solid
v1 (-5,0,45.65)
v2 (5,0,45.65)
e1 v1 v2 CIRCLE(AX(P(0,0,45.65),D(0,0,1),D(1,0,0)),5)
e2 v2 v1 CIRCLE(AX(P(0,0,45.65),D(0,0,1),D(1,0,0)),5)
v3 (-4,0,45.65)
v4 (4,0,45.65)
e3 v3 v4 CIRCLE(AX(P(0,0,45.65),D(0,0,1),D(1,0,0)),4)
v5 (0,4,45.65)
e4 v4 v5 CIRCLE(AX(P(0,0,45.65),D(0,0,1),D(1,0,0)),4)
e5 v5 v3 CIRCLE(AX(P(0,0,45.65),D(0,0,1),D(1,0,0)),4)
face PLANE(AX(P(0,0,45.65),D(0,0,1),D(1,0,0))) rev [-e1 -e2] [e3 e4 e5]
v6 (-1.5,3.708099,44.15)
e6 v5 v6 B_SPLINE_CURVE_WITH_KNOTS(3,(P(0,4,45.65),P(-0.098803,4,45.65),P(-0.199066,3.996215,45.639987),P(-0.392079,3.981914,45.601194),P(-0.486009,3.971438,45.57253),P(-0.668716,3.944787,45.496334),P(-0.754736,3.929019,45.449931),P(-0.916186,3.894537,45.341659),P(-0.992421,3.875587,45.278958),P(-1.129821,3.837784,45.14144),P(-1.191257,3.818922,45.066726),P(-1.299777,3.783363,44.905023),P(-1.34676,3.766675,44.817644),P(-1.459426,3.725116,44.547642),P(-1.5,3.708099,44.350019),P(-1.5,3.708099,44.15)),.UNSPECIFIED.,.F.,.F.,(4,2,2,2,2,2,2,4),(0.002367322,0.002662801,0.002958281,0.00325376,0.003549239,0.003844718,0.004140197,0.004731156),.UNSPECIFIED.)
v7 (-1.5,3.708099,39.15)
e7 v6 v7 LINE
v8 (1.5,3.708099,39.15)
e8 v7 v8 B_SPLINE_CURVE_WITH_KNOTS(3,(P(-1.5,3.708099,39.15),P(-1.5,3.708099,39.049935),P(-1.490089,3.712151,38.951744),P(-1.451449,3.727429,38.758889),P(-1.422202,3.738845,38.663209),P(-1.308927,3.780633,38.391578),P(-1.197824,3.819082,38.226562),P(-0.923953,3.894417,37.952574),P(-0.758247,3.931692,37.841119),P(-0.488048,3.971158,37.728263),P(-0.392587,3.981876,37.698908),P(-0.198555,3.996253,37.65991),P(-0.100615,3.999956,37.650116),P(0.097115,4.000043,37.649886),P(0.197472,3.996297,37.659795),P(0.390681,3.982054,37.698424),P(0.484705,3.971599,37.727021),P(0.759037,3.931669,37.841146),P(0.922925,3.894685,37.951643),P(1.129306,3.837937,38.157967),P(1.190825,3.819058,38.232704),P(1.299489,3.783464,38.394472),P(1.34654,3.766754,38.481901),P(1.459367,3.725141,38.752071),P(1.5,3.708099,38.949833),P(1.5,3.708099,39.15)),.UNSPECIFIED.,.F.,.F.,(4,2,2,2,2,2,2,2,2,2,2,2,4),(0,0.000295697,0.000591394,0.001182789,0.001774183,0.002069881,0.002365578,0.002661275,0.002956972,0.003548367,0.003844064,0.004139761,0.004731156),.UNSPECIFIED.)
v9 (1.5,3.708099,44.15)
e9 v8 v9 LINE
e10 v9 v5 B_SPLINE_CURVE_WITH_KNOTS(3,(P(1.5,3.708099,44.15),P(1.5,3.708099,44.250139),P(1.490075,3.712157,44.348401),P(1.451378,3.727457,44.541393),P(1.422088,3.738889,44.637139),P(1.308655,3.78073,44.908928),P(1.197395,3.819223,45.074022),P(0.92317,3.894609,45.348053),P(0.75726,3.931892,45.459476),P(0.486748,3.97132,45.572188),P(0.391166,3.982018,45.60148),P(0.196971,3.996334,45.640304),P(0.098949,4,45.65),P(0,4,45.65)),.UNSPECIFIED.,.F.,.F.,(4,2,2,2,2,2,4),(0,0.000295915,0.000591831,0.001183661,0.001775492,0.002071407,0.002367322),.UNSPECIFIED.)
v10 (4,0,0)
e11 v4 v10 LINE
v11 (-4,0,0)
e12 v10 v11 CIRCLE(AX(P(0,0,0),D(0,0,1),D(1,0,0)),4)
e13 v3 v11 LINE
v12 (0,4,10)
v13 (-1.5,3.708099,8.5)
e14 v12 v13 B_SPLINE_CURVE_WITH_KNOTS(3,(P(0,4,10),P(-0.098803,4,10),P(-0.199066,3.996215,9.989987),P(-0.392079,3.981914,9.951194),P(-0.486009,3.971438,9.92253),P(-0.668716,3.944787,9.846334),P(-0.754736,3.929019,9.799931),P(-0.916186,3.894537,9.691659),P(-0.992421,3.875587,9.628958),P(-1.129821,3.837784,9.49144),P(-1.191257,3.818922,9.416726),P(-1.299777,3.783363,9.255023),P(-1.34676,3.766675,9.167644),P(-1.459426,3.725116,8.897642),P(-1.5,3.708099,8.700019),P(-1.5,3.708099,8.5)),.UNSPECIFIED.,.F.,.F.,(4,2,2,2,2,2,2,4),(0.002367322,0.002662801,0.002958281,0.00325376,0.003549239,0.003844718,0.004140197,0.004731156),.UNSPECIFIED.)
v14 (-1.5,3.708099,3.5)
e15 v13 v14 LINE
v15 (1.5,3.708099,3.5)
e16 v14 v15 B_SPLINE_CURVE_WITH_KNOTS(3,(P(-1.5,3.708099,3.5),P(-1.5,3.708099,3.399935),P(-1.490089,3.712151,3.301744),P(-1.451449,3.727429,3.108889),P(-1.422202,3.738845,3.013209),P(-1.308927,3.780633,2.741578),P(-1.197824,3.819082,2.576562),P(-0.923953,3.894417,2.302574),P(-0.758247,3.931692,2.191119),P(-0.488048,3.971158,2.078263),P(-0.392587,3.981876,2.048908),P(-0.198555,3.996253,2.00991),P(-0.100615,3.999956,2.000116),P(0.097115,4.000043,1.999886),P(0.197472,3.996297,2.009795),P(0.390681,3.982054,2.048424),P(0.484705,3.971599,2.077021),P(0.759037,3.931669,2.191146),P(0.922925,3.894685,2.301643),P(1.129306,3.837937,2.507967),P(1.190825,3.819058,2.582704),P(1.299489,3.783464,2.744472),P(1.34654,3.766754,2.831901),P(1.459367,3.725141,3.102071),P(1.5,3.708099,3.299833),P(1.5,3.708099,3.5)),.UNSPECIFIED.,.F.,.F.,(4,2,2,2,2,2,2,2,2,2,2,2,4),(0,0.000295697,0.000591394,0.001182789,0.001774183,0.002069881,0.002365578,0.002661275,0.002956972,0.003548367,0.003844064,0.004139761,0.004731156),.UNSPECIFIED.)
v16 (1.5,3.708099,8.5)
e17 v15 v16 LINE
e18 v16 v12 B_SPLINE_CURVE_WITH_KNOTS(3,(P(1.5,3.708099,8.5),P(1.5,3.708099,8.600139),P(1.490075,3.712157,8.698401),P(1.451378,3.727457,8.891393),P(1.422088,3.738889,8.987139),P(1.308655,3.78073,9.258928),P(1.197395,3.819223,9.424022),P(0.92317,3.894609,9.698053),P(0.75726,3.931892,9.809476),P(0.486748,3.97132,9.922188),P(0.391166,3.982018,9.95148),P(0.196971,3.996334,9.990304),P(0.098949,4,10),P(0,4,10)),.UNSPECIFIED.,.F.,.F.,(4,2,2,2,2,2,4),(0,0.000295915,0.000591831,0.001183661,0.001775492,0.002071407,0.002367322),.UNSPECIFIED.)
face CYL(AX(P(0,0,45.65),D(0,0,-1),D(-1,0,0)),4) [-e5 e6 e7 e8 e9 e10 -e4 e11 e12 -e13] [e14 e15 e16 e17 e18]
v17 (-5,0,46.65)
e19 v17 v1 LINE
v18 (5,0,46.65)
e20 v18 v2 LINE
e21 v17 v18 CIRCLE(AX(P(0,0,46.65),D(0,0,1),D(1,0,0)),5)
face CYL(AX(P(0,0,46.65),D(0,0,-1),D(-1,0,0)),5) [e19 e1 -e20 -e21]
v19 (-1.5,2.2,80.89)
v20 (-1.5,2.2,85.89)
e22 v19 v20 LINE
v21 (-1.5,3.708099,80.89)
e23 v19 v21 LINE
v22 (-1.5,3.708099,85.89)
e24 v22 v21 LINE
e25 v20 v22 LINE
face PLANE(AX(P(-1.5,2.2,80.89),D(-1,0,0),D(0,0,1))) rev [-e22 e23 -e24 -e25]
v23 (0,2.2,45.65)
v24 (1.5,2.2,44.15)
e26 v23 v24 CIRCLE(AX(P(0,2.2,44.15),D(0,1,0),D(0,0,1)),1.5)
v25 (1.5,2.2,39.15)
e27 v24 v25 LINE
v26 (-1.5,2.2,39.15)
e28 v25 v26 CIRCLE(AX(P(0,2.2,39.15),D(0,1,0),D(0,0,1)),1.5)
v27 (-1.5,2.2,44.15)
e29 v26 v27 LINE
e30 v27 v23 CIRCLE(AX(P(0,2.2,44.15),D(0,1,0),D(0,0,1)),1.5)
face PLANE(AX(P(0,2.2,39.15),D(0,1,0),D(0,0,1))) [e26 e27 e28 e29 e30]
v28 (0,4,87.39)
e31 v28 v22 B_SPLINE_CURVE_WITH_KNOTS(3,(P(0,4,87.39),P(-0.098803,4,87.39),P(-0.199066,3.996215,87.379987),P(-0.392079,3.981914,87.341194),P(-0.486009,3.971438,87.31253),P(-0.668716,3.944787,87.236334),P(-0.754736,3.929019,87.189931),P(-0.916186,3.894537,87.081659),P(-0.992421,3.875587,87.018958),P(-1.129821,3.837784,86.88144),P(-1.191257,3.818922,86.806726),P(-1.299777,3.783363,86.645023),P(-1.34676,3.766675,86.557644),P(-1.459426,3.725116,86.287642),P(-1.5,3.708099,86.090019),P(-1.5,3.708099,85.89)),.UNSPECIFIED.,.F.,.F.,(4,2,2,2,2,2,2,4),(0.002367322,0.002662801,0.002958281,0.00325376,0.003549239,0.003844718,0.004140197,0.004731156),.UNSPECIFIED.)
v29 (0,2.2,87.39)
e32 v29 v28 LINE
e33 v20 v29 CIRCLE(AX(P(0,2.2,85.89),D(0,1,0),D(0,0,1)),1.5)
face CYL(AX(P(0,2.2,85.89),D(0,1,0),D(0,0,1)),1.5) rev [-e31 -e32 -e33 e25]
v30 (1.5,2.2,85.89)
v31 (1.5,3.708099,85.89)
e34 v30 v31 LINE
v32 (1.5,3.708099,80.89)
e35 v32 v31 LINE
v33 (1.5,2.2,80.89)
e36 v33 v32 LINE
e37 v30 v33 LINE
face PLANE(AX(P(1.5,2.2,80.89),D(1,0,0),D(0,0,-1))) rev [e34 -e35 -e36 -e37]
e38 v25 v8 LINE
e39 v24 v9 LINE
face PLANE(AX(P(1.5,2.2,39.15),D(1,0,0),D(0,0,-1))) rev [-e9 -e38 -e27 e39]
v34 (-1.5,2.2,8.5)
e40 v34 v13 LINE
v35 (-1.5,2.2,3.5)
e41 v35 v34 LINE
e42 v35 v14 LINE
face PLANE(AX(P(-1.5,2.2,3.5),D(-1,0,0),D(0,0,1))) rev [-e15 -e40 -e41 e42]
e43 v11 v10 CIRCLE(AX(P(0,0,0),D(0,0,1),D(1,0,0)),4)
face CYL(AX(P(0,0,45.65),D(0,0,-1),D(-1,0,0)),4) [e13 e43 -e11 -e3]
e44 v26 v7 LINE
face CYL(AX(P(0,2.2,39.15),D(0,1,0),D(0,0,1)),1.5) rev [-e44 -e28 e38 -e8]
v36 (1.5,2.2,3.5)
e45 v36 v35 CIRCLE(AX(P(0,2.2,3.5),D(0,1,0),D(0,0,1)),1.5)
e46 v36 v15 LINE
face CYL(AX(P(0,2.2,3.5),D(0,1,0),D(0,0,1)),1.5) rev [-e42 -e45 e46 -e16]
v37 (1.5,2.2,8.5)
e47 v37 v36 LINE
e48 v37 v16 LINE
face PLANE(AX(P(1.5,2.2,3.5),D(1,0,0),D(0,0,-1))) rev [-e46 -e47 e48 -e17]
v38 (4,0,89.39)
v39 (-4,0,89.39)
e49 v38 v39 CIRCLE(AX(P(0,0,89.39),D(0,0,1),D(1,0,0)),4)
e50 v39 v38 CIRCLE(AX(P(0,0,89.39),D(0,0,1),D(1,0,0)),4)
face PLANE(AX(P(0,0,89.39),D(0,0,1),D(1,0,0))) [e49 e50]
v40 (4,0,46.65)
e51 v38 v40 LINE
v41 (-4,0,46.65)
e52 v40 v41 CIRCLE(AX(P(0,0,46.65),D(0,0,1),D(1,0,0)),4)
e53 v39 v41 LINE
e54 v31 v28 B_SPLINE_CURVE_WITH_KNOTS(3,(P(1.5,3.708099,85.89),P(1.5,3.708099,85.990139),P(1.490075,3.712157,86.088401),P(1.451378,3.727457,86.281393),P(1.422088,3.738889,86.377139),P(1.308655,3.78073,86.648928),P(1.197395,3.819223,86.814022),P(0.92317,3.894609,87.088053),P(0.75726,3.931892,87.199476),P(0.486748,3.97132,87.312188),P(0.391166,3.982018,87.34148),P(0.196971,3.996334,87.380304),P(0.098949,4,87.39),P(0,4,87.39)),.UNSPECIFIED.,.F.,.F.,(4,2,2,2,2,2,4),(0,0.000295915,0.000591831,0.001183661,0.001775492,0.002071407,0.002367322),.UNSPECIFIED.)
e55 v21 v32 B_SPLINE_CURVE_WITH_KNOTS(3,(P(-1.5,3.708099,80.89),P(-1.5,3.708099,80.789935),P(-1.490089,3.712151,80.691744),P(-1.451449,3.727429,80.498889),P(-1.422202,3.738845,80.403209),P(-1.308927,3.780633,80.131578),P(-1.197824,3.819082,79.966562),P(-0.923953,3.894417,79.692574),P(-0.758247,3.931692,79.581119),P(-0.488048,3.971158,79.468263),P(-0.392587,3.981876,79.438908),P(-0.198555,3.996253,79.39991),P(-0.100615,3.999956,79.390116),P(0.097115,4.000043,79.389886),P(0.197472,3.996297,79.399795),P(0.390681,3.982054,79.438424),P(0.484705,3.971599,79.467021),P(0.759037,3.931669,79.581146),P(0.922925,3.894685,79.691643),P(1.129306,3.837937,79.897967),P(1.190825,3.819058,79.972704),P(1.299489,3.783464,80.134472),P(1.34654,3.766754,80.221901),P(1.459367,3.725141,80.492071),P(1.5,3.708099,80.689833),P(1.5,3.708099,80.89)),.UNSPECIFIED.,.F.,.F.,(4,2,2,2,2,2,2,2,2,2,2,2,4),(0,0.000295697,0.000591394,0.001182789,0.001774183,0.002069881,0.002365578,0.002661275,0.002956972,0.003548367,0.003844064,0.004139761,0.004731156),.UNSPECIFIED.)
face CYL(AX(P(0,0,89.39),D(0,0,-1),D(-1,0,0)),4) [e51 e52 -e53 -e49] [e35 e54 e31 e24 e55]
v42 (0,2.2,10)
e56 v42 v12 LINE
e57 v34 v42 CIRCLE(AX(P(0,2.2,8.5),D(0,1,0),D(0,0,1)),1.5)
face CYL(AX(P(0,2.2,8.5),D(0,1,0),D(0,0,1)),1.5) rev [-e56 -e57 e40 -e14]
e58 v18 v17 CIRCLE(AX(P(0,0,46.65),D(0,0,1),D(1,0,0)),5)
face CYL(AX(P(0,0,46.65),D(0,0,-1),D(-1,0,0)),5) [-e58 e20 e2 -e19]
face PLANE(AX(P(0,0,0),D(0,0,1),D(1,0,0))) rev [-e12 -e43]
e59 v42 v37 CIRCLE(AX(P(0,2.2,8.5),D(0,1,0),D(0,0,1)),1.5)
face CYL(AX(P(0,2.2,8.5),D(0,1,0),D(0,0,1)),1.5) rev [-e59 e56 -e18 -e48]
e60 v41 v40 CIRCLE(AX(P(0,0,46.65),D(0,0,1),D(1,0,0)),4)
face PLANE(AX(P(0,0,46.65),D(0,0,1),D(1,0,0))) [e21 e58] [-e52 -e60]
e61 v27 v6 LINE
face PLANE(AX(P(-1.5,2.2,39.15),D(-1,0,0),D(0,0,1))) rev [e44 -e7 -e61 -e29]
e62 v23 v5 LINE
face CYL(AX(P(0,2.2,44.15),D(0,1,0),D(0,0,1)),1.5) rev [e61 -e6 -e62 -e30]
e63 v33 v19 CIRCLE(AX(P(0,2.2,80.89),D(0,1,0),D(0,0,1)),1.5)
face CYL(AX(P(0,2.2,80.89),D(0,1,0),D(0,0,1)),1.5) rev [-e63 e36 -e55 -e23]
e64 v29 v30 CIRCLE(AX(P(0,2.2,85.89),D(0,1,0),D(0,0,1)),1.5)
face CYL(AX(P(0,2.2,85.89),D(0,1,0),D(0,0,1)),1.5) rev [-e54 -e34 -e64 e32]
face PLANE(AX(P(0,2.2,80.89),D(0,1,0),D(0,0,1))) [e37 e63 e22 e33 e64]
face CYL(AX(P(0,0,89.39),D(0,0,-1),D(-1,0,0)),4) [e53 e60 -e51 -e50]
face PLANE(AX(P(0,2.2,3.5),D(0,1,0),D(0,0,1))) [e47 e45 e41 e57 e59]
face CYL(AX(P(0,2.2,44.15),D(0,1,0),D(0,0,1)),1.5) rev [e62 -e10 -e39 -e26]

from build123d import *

# Parameters (mm, degrees)
SKETCH1_R           = 4
BOSS_EXTRUDE1_DEPTH = 45.65
SKETCH2_R           = 5
BOSS_EXTRUDE2_DEPTH = 1
SKETCH3_R           = 4
BOSS_EXTRUDE3_DEPTH = 42.74
CUT_EXTRUDE1_DEPTH  = 1.8


with BuildPart() as part:
    # Sketch1 → Boss-Extrude1 (new body)
    with BuildSketch(Plane.XY):
        Circle(SKETCH1_R)
    extrude(amount=BOSS_EXTRUDE1_DEPTH)

    # Sketch2 → Boss-Extrude2 (add)
    with BuildSketch(Plane.XY.offset(45.65)):
        Circle(SKETCH2_R)
    extrude(amount=BOSS_EXTRUDE2_DEPTH)

    # Sketch3 → Boss-Extrude3 (add)
    with BuildSketch(Plane.XY.offset(46.65)):
        Circle(SKETCH3_R)
    extrude(amount=BOSS_EXTRUDE3_DEPTH)

    # Sketch4 → Cut-Extrude1 (cut)
    with BuildSketch(Plane(origin=(0, 4, 0), x_dir=(1, 0, 0), z_dir=(0, 1, 0))):
        with BuildLine():
            Line((1.5, -3.5), (1.5, -8.5))
            ThreePointArc((1.5, -8.5), (0, -10), (-1.5, -8.5))
            Line((-1.5, -8.5), (-1.5, -3.5))
            ThreePointArc((-1.5, -3.5), (0, -2), (1.5, -3.5))
        make_face()
        with BuildLine():
            Line((1.5, -39.15), (1.5, -44.15))
            ThreePointArc((1.5, -44.15), (0, -45.65), (-1.5, -44.15))
            Line((-1.5, -44.15), (-1.5, -39.15))
            ThreePointArc((-1.5, -39.15), (0, -37.65), (1.5, -39.15))
        make_face()
        with BuildLine():
            Line((1.5, -80.89), (1.5, -85.89))
            ThreePointArc((1.5, -85.89), (0, -87.39), (-1.5, -85.89))
            Line((-1.5, -85.89), (-1.5, -80.89))
            ThreePointArc((-1.5, -80.89), (0, -79.39), (1.5, -80.89))
        make_face()
    extrude(amount=-CUT_EXTRUDE1_DEPTH, mode=Mode.SUBTRACT)


solid = part.part
